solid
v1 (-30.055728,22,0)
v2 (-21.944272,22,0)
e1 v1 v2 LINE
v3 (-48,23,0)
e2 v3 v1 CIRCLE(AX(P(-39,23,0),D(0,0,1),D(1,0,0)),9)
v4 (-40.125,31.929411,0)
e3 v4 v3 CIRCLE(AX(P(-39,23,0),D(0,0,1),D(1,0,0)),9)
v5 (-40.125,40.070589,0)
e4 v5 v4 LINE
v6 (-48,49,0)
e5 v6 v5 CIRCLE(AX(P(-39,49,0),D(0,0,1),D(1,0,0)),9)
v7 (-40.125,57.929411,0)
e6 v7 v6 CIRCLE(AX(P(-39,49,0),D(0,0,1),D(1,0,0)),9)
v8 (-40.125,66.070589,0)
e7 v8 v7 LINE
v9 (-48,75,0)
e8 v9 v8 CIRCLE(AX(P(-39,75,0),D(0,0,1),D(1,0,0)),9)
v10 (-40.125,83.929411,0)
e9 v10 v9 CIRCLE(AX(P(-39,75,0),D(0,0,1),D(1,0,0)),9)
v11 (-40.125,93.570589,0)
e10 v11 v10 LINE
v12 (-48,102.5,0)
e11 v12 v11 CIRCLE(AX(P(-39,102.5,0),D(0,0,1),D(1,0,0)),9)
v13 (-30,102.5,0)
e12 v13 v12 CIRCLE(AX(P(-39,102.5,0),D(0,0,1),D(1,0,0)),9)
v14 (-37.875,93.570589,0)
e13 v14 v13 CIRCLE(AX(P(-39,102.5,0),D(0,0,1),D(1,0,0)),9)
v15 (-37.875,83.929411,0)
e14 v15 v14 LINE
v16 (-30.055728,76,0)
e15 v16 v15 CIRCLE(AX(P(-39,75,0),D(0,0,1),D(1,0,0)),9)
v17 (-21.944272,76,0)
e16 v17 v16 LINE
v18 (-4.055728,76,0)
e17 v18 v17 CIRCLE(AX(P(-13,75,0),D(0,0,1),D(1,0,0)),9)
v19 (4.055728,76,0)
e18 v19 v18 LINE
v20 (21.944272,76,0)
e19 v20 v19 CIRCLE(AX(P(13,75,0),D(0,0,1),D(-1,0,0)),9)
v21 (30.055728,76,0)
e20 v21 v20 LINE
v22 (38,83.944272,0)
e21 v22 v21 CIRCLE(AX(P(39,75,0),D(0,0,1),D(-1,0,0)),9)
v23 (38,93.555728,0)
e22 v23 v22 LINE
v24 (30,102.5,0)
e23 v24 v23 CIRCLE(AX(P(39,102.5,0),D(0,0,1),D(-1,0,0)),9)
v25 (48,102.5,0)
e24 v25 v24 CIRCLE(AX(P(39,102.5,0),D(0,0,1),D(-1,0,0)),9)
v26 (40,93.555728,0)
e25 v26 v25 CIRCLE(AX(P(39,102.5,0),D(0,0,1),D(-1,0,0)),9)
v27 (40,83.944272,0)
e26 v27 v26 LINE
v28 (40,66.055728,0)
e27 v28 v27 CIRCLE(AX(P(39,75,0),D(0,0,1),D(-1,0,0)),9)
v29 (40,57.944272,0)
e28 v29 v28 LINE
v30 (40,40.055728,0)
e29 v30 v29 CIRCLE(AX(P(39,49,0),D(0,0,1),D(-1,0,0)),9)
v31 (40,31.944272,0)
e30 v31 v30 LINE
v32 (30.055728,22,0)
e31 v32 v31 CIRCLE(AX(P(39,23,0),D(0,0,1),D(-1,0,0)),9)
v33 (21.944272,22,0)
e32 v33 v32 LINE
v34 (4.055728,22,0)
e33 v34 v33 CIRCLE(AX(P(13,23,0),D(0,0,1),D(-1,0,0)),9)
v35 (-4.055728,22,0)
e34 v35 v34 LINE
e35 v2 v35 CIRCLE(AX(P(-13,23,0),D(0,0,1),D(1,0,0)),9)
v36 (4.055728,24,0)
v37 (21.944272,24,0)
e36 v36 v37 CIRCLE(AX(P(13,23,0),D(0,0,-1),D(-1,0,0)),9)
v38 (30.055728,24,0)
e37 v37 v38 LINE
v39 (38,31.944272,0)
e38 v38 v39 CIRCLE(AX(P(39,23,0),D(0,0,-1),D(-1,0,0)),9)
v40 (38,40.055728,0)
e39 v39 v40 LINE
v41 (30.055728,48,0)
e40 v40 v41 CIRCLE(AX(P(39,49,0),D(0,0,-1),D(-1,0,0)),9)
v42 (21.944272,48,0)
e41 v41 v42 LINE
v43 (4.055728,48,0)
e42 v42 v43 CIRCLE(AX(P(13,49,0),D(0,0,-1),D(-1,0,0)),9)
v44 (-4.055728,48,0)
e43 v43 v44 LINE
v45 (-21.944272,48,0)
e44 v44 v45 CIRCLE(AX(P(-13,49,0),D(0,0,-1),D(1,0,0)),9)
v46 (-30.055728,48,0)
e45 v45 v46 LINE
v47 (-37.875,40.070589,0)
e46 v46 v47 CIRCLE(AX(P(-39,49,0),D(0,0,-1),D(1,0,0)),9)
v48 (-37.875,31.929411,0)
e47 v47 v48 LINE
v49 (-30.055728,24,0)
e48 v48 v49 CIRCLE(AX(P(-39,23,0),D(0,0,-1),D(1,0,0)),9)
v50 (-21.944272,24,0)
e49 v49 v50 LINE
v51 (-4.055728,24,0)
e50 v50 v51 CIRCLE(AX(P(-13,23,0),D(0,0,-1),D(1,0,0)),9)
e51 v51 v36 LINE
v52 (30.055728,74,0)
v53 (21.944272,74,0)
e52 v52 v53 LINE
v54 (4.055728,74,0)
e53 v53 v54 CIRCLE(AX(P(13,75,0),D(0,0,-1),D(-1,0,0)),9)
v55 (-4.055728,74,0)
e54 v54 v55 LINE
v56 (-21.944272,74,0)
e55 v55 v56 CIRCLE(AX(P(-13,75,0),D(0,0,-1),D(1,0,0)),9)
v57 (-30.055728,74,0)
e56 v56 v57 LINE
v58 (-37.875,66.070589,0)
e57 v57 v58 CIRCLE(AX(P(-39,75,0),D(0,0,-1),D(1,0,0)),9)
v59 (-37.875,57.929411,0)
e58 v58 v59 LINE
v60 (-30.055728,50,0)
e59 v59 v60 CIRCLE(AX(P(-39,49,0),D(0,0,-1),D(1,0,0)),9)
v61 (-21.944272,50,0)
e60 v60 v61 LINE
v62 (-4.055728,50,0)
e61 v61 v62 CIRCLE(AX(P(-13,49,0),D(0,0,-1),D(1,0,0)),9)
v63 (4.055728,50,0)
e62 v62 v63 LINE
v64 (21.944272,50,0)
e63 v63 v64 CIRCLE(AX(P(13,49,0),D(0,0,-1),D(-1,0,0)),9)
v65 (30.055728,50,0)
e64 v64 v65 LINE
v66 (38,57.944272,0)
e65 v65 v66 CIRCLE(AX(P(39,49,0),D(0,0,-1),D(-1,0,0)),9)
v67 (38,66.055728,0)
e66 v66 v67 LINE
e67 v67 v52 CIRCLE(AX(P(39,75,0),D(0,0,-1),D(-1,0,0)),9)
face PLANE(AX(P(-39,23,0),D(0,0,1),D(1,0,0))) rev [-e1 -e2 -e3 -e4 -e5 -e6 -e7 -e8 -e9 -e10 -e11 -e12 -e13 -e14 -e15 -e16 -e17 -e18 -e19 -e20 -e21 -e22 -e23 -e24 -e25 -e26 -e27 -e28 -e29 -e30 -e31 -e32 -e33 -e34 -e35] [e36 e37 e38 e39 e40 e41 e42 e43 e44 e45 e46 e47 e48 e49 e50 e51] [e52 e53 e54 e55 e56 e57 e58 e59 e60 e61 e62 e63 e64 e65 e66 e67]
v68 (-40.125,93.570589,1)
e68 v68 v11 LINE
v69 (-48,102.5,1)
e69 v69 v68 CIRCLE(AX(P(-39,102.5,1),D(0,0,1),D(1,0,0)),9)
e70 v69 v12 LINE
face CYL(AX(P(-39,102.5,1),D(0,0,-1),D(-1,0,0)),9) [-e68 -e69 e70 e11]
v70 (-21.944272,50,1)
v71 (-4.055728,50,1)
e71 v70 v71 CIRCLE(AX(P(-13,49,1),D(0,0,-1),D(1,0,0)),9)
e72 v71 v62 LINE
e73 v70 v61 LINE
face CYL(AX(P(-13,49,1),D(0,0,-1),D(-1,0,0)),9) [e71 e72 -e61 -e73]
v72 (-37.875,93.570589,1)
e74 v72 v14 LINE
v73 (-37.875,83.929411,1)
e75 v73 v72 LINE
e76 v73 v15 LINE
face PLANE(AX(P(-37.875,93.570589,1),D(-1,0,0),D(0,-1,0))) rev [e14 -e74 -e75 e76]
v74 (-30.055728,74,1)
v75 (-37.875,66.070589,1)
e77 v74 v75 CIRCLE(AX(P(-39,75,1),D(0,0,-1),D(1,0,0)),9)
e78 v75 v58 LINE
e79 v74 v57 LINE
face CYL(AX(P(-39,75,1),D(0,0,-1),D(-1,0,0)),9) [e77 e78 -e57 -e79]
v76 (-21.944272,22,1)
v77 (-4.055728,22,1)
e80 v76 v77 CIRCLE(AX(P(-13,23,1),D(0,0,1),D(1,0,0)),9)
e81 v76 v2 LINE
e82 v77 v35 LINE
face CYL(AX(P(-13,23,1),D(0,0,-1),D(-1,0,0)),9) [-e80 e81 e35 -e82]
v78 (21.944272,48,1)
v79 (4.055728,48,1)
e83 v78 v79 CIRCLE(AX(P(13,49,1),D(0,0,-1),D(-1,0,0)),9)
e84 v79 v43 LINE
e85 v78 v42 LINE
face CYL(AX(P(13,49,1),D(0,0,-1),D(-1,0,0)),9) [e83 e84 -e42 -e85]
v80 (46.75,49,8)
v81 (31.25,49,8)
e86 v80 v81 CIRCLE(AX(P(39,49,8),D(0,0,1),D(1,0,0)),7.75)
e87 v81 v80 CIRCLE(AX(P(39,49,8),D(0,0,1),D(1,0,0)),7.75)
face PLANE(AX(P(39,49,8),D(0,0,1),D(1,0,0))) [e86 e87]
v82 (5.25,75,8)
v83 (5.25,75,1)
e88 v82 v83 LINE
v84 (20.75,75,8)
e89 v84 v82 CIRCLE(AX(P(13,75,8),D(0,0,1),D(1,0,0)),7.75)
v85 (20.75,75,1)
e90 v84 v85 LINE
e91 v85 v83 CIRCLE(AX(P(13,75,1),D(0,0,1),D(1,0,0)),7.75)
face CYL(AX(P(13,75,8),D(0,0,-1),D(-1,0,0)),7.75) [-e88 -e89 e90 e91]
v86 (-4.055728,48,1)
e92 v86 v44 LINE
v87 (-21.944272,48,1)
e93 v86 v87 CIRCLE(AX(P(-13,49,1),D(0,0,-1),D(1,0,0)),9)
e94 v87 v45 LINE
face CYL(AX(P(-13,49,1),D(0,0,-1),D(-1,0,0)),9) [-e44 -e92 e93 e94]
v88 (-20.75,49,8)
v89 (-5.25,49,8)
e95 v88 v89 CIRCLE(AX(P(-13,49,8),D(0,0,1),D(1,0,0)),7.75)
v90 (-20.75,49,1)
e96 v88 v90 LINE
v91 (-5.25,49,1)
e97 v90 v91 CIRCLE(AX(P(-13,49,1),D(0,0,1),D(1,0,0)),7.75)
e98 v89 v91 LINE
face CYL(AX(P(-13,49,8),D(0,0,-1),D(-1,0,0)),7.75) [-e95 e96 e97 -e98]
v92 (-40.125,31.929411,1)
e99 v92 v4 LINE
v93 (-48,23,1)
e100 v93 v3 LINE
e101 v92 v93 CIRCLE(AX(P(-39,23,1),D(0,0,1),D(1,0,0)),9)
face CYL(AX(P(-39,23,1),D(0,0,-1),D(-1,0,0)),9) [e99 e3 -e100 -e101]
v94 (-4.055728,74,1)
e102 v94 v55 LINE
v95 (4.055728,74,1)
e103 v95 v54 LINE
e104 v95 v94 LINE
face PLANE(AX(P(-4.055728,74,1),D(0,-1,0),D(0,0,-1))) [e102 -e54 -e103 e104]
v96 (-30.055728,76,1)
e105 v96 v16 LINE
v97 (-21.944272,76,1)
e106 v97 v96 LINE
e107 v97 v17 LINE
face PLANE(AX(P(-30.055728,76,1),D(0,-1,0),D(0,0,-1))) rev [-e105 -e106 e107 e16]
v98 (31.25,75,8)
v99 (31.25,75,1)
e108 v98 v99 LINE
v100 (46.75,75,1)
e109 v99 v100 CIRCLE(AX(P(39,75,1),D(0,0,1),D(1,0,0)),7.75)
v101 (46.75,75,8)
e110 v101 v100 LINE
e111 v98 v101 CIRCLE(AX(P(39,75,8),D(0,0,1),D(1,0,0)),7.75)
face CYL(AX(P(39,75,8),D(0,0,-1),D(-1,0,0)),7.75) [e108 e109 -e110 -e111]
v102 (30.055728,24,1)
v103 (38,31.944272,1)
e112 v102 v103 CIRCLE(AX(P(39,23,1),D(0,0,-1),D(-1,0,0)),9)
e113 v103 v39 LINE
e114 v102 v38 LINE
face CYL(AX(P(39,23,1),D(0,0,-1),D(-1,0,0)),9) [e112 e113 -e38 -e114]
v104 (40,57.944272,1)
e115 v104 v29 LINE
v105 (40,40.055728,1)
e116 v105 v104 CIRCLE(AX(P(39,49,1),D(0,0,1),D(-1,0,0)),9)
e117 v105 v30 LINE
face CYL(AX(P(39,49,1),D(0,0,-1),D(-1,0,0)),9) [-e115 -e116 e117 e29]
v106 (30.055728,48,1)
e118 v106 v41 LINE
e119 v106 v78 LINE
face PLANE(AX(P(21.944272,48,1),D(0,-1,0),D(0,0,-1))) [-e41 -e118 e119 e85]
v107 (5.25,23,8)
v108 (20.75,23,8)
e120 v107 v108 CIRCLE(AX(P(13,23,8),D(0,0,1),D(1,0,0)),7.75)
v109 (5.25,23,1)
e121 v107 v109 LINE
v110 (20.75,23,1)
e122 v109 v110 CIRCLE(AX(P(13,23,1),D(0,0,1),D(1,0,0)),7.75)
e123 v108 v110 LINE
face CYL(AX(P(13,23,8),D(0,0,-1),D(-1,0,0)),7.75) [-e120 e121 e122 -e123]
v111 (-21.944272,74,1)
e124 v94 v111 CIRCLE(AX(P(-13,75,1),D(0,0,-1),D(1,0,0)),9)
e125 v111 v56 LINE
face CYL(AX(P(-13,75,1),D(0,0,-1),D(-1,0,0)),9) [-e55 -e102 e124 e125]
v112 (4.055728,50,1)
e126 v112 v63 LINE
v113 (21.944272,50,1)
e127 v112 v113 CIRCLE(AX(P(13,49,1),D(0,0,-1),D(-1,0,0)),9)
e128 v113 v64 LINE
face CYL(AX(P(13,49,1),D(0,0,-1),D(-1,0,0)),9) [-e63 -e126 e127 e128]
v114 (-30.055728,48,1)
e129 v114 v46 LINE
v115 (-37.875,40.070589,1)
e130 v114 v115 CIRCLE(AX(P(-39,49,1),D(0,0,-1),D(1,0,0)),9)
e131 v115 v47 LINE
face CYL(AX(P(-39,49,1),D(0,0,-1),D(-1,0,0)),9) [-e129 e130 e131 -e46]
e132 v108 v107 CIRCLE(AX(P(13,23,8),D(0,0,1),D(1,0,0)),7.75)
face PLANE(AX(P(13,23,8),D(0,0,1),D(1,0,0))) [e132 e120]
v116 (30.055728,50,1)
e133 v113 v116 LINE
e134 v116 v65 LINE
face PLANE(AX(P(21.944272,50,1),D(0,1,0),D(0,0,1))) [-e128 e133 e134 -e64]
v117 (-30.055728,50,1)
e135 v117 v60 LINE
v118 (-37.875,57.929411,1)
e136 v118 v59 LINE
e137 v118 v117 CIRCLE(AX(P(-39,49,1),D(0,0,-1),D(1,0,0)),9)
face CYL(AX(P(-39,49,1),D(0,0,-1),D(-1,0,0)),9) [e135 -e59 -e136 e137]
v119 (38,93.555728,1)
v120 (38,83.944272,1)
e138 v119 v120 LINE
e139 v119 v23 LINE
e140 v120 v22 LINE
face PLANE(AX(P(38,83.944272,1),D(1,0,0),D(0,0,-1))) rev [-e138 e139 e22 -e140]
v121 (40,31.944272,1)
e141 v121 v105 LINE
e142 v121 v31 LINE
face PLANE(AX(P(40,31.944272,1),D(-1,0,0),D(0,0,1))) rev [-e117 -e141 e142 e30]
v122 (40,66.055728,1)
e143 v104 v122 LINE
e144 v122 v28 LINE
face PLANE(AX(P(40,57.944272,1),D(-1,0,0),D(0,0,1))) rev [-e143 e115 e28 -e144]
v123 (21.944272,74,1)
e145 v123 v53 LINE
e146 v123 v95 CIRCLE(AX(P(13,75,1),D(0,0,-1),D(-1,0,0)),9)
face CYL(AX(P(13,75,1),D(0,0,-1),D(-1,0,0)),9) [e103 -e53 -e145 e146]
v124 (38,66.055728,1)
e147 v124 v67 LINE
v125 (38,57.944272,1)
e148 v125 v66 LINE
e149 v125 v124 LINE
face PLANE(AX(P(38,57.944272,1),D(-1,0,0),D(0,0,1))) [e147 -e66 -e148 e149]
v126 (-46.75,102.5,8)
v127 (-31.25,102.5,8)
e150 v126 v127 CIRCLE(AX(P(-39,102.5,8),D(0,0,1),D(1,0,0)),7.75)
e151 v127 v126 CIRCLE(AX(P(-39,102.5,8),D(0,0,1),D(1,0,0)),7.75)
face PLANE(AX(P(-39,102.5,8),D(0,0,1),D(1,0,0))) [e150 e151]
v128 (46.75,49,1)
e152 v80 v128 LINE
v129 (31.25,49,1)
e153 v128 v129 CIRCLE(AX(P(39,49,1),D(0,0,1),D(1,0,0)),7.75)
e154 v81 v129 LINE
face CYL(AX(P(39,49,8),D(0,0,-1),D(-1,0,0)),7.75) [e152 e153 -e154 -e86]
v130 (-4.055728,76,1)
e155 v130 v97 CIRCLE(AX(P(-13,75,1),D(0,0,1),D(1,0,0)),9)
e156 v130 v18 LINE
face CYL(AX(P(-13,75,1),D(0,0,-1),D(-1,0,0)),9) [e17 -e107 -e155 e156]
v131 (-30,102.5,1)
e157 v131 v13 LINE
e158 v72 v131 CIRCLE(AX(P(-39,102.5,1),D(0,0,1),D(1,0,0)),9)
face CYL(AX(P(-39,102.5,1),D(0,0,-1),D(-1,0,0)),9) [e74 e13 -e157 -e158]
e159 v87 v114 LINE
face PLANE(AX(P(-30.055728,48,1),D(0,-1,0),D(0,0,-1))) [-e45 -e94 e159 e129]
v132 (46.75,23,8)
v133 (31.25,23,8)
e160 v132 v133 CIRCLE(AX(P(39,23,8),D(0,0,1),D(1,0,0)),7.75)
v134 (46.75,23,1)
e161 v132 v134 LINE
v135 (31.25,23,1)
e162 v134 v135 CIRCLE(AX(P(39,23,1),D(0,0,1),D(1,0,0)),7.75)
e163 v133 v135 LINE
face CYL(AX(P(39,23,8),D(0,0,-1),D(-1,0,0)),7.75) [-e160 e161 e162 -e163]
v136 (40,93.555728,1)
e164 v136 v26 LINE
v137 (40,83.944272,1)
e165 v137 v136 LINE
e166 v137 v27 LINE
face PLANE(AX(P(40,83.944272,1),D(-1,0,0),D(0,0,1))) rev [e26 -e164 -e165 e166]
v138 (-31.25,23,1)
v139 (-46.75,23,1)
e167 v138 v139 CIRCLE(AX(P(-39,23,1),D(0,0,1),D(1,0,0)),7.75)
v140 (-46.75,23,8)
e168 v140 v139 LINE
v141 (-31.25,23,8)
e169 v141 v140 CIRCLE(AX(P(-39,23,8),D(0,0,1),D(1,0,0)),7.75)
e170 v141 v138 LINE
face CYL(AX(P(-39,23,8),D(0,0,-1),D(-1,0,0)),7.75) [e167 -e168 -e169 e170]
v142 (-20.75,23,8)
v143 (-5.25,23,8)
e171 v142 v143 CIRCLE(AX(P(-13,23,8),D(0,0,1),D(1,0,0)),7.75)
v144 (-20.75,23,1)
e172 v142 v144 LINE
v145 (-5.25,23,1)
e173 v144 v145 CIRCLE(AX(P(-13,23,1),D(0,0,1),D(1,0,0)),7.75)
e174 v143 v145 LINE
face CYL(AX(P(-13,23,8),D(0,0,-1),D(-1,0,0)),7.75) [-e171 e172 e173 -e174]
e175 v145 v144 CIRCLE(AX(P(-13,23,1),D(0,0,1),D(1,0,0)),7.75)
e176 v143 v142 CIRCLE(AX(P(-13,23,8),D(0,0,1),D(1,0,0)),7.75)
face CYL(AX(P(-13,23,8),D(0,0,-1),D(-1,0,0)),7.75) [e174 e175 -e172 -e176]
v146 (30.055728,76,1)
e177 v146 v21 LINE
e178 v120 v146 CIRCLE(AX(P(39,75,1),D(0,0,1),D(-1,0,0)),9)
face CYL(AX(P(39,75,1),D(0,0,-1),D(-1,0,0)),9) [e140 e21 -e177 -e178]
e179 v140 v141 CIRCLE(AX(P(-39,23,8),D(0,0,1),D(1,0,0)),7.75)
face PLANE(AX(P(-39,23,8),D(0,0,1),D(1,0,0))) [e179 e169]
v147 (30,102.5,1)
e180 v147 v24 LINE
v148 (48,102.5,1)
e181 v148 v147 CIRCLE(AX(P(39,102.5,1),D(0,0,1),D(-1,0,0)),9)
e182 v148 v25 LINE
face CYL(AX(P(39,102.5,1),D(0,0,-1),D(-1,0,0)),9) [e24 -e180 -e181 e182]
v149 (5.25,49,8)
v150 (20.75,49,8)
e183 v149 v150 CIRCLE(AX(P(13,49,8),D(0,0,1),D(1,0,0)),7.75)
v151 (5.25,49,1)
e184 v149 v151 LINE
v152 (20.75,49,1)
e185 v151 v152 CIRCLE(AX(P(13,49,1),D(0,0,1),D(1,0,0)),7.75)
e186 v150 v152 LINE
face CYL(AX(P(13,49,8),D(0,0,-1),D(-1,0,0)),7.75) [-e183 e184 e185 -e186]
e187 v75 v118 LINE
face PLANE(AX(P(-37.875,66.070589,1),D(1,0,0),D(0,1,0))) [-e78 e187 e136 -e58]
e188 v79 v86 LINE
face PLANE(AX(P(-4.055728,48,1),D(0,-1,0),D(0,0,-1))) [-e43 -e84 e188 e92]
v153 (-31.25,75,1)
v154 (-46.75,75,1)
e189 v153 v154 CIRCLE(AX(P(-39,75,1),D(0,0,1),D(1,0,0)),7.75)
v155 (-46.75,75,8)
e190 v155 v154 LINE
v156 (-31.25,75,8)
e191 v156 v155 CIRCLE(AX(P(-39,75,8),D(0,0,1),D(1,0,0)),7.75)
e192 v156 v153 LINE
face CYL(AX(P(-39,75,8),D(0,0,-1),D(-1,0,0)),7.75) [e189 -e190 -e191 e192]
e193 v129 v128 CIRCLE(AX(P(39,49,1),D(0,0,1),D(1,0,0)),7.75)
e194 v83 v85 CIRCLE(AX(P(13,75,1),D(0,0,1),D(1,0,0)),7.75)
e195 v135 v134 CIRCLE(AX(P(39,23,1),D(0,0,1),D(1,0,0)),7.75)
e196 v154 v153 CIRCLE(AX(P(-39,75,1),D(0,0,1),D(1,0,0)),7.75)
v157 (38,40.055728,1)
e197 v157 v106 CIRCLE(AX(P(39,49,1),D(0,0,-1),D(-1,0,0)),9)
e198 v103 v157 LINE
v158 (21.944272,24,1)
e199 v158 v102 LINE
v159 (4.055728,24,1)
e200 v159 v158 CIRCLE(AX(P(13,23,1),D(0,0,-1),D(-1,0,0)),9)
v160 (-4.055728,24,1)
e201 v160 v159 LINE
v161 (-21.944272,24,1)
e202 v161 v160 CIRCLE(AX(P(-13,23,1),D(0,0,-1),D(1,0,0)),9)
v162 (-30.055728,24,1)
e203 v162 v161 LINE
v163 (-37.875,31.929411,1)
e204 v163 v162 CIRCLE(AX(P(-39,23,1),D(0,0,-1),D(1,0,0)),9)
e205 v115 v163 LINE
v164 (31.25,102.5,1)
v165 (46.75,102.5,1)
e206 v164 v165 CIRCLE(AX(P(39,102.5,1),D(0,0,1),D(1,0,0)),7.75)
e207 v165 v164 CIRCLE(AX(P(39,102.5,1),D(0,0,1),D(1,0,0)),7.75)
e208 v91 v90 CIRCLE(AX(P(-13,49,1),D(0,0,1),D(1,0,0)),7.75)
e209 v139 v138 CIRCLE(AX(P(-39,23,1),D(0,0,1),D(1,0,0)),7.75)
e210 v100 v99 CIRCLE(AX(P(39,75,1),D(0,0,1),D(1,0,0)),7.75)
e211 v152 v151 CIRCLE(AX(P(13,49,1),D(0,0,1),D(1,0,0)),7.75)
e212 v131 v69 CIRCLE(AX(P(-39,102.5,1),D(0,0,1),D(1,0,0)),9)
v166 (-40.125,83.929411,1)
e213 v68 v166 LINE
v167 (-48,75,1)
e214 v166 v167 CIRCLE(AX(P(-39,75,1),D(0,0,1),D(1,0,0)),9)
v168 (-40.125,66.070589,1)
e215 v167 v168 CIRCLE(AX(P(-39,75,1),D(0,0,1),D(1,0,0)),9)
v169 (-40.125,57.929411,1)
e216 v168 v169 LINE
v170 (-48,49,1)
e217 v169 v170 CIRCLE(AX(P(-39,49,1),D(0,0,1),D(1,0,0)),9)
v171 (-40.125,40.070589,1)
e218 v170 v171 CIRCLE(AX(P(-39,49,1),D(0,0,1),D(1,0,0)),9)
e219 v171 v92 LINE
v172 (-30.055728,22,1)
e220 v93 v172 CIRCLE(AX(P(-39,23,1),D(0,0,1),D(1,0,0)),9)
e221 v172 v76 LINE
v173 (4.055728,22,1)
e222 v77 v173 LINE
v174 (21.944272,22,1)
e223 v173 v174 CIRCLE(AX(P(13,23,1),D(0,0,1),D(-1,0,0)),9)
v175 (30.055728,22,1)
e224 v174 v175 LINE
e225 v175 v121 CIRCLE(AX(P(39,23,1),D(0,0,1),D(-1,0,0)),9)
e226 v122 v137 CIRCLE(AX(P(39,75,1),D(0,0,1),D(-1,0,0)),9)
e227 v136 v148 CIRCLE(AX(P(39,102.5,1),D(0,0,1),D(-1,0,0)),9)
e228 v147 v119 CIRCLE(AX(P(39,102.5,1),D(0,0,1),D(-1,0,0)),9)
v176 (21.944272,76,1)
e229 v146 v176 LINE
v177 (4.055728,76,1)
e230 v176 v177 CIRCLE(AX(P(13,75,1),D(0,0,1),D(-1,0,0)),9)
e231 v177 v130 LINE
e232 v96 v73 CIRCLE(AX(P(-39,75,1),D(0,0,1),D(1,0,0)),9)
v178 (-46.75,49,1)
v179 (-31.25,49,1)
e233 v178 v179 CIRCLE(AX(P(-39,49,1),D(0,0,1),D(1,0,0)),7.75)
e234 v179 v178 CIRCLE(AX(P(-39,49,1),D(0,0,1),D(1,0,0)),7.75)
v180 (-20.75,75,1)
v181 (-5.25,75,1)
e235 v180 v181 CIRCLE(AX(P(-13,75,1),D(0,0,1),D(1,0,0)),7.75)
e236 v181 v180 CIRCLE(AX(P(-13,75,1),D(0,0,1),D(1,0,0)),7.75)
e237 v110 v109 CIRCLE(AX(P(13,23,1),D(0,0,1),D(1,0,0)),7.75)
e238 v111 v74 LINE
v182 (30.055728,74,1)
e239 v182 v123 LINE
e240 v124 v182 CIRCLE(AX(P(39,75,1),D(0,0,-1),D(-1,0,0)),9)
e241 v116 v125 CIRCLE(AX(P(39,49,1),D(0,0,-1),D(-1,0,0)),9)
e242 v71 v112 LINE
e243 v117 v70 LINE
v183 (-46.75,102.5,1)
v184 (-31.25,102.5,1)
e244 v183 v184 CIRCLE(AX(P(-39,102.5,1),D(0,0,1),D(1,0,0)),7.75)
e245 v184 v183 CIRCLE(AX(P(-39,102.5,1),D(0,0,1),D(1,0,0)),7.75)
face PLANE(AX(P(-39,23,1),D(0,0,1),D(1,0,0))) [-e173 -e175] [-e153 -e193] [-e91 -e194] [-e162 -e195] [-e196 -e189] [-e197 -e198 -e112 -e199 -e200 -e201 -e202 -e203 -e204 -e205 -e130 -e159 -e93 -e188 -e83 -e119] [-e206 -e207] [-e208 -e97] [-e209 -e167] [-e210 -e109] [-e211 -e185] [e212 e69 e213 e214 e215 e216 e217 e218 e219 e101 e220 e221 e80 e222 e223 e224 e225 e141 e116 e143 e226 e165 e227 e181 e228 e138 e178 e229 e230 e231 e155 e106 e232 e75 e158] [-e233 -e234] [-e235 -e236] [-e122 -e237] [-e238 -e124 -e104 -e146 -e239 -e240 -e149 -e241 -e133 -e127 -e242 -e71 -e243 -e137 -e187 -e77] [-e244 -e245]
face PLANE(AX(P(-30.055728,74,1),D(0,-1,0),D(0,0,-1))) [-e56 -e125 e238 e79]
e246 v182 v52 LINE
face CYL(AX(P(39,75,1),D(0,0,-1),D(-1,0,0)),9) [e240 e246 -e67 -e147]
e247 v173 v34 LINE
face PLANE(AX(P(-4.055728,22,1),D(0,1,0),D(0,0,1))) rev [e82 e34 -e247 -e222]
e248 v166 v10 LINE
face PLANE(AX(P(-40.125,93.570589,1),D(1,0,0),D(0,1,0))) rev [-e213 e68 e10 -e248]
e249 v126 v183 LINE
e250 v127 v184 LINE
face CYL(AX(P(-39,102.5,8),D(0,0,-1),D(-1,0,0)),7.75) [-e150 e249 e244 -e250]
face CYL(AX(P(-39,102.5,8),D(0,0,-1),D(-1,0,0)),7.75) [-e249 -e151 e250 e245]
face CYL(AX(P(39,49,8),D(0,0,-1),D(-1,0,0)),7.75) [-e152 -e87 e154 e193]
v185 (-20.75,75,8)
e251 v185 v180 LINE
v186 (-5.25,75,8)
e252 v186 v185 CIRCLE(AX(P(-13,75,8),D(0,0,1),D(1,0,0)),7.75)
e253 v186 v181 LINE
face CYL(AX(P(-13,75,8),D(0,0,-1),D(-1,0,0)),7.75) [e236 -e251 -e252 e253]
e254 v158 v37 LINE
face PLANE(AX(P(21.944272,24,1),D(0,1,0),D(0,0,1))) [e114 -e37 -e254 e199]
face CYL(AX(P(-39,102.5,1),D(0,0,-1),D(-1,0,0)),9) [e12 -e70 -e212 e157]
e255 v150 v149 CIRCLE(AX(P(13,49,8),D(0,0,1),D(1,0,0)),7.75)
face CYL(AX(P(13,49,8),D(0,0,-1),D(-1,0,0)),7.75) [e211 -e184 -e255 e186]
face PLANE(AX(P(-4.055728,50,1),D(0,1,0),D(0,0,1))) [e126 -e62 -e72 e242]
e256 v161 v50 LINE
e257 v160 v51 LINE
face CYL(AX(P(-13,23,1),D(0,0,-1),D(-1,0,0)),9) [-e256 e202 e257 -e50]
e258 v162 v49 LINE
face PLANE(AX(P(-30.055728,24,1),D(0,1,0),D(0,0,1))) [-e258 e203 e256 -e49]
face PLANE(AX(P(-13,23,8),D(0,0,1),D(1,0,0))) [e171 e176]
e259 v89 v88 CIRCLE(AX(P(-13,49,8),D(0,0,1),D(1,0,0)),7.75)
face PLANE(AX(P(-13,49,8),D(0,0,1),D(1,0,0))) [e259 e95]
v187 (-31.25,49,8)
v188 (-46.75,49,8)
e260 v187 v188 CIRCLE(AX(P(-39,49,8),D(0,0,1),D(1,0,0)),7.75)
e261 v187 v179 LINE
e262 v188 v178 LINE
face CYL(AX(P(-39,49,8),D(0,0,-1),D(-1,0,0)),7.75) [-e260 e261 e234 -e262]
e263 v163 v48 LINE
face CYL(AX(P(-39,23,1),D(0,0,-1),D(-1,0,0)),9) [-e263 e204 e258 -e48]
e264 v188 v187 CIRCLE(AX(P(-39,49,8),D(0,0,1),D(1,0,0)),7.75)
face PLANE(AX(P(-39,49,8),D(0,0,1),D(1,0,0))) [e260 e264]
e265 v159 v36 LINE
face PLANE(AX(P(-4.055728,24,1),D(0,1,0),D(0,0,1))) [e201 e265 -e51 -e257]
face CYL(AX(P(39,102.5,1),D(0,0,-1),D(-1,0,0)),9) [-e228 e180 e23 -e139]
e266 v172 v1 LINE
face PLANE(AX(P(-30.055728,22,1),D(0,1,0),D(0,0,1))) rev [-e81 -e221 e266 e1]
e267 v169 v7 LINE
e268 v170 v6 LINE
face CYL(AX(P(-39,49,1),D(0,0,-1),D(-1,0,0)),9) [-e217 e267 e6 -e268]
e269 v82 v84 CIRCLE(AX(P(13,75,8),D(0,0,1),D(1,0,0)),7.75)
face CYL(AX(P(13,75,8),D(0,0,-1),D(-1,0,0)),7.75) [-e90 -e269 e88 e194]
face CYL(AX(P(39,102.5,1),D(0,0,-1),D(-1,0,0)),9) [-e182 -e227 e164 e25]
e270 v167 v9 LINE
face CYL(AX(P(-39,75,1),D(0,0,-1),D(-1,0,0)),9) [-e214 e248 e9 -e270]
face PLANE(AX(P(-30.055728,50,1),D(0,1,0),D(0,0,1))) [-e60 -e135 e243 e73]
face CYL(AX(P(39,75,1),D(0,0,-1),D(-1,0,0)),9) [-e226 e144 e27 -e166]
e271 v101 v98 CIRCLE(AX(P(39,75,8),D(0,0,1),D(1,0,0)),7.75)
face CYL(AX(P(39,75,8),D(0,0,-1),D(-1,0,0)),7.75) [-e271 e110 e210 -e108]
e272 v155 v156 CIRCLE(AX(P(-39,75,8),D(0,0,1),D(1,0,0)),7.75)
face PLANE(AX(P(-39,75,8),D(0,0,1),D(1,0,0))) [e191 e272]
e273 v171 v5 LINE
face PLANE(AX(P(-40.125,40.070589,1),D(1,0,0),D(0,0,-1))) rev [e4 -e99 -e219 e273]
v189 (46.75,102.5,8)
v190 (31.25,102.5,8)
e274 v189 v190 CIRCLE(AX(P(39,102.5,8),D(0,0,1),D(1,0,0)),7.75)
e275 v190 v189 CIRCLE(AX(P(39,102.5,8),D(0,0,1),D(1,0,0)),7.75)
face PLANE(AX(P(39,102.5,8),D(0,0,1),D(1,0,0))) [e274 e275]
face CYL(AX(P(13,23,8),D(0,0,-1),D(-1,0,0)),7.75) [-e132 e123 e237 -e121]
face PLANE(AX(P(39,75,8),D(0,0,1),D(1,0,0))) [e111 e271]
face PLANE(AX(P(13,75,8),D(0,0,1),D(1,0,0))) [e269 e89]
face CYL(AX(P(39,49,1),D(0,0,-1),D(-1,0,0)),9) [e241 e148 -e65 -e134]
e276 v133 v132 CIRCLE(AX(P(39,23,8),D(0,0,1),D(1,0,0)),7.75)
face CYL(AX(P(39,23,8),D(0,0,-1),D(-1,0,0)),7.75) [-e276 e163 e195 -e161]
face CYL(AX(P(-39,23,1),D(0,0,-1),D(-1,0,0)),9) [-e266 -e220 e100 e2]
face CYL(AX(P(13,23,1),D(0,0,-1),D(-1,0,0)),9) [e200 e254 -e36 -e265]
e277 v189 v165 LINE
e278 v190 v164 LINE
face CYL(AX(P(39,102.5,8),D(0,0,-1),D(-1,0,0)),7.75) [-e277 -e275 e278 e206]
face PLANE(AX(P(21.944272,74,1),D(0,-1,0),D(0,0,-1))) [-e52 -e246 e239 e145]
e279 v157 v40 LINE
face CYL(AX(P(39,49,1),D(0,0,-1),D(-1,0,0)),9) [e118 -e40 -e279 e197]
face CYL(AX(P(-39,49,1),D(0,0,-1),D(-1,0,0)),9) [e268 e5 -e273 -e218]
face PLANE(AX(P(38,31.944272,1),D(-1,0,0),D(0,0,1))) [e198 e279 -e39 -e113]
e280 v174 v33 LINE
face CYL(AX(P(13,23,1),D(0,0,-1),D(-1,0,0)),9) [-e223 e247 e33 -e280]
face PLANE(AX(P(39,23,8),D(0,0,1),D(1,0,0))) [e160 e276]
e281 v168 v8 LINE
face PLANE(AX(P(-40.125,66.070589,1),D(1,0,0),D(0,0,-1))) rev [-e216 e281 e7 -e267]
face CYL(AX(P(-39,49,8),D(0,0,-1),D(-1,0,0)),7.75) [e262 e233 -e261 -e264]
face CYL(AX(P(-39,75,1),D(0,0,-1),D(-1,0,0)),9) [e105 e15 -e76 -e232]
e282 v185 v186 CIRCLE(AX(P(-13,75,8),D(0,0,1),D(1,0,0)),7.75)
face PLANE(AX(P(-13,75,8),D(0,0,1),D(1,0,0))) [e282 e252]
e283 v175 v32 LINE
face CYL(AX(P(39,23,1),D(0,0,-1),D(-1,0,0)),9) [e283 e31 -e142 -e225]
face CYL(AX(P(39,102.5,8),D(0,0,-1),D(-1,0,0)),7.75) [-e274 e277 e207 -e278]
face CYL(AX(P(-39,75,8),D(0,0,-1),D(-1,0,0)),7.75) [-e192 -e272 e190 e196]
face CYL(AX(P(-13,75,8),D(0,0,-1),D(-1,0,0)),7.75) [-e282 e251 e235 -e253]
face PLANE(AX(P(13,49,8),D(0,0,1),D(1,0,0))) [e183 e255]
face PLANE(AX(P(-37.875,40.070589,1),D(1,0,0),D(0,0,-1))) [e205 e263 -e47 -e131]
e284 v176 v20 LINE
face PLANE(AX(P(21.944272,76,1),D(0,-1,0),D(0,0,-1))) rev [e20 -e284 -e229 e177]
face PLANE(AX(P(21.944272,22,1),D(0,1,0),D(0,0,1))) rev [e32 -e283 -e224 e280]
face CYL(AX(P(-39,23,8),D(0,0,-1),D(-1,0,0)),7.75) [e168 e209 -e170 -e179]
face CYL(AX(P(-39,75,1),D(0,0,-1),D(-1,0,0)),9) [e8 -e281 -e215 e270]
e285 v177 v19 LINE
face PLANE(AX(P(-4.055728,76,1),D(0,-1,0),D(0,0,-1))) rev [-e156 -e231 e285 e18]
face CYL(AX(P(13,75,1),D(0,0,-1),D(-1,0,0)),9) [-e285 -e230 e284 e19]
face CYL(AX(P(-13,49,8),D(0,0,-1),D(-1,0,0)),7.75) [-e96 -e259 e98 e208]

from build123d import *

# Parameters (mm, degrees)
BOSS_EXTRUDE1_DEPTH = 1
SKETCH2_R           = 7.75
BOSS_EXTRUDE2_DEPTH = 7


with BuildPart() as part:
    # Sketch1 → Boss-Extrude1 (new body)
    with BuildSketch(Plane.XY):
        with BuildLine():
            Line((-40.125, 93.570589325), (-40.125, 83.929410675))
            ThreePointArc((-40.125, 83.929410675), (-48, 75), (-40.125, 66.070589325))
            Line((-40.125, 66.070589325), (-40.125, 57.929410675))
            ThreePointArc((-40.125, 57.929410675), (-48, 49), (-40.125, 40.070589325))
            Line((-40.125, 40.070589325), (-40.125, 31.929410675))
            ThreePointArc((-40.125, 31.929410675), (-45.319299992, 16.591689176), (-30.05572809, 22))
            Line((-30.05572809, 22), (-21.94427191, 22))
            ThreePointArc((-21.94427191, 22), (-13, 14), (-4.05572809, 22))
            Line((-4.05572809, 22), (4.05572809, 22))
            ThreePointArc((4.05572809, 22), (13, 14), (21.94427191, 22))
            Line((21.94427191, 22), (30.05572809, 22))
            ThreePointArc((30.05572809, 22), (45.363961031, 16.636038969), (40, 31.94427191))
            Line((40, 31.94427191), (40, 40.05572809))
            ThreePointArc((40, 40.05572809), (48, 49), (40, 57.94427191))
            Line((40, 57.94427191), (40, 66.05572809))
            ThreePointArc((40, 66.05572809), (48, 75), (40, 83.94427191))
            Line((40, 83.94427191), (40, 93.55572809))
            ThreePointArc((40, 93.55572809), (39, 111.5), (38, 93.55572809))
            Line((38, 93.55572809), (38, 83.94427191))
            ThreePointArc((38, 83.94427191), (32.636038969, 81.363961031), (30.05572809, 76))
            Line((30.05572809, 76), (21.94427191, 76))
            ThreePointArc((21.94427191, 76), (13, 84), (4.05572809, 76))
            Line((4.05572809, 76), (-4.05572809, 76))
            ThreePointArc((-4.05572809, 76), (-13, 84), (-21.94427191, 76))
            Line((-21.94427191, 76), (-30.05572809, 76))
            ThreePointArc((-30.05572809, 76), (-32.591689176, 81.319299992), (-37.875, 83.929410675))
            Line((-37.875, 83.929410675), (-37.875, 93.570589325))
            ThreePointArc((-37.875, 93.570589325), (-39, 111.5), (-40.125, 93.570589325))
        make_face()
        with BuildLine():
            Line((-30.05572809, 74), (-21.94427191, 74))
            ThreePointArc((-21.94427191, 74), (-13, 66), (-4.05572809, 74))
            Line((-4.05572809, 74), (4.05572809, 74))
            ThreePointArc((4.05572809, 74), (13, 66), (21.94427191, 74))
            Line((21.94427191, 74), (30.05572809, 74))
            ThreePointArc((30.05572809, 74), (32.636038969, 68.636038969), (38, 66.05572809))
            Line((38, 66.05572809), (38, 57.94427191))
            ThreePointArc((38, 57.94427191), (32.636038969, 55.363961031), (30.05572809, 50))
            Line((30.05572809, 50), (21.94427191, 50))
            ThreePointArc((21.94427191, 50), (13, 58), (4.05572809, 50))
            Line((4.05572809, 50), (-4.05572809, 50))
            ThreePointArc((-4.05572809, 50), (-13, 58), (-21.94427191, 50))
            Line((-21.94427191, 50), (-30.05572809, 50))
            ThreePointArc((-30.05572809, 50), (-32.591689176, 55.319299992), (-37.875, 57.929410675))
            Line((-37.875, 57.929410675), (-37.875, 66.070589325))
            ThreePointArc((-37.875, 66.070589325), (-32.591689176, 68.680700008), (-30.05572809, 74))
        make_face(mode=Mode.SUBTRACT)
        with BuildLine():
            Line((-30.05572809, 48), (-21.94427191, 48))
            ThreePointArc((-21.94427191, 48), (-13, 40), (-4.05572809, 48))
            Line((-4.05572809, 48), (4.05572809, 48))
            ThreePointArc((4.05572809, 48), (13, 40), (21.94427191, 48))
            Line((21.94427191, 48), (30.05572809, 48))
            ThreePointArc((30.05572809, 48), (32.636038969, 42.636038969), (38, 40.05572809))
            Line((38, 40.05572809), (38, 31.94427191))
            ThreePointArc((38, 31.94427191), (32.636038969, 29.363961031), (30.05572809, 24))
            Line((30.05572809, 24), (21.94427191, 24))
            ThreePointArc((21.94427191, 24), (13, 32), (4.05572809, 24))
            Line((4.05572809, 24), (-4.05572809, 24))
            ThreePointArc((-4.05572809, 24), (-13, 32), (-21.94427191, 24))
            Line((-21.94427191, 24), (-30.05572809, 24))
            ThreePointArc((-30.05572809, 24), (-32.591689176, 29.319299992), (-37.875, 31.929410675))
            Line((-37.875, 31.929410675), (-37.875, 40.070589325))
            ThreePointArc((-37.875, 40.070589325), (-32.591689176, 42.680700008), (-30.05572809, 48))
        make_face(mode=Mode.SUBTRACT)
    extrude(amount=BOSS_EXTRUDE1_DEPTH)

    # Sketch2 → Boss-Extrude2 (add)
    with BuildSketch(Plane.XY.offset(1)):
        with Locations((-39, 102.5)):
            Circle(SKETCH2_R)
        with Locations((-39, 75)):
            Circle(SKETCH2_R)
        with Locations((-39, 49)):
            Circle(SKETCH2_R)
        with Locations((-39, 23)):
            Circle(SKETCH2_R)
        with Locations((-13, 75)):
            Circle(SKETCH2_R)
        with Locations((-13, 49)):
            Circle(SKETCH2_R)
        with Locations((-13, 23)):
            Circle(SKETCH2_R)
        with Locations((13, 75)):
            Circle(SKETCH2_R)
        with Locations((39, 102.5)):
            Circle(SKETCH2_R)
        with Locations((39, 23)):
            Circle(SKETCH2_R)
        with Locations((13, 23)):
            Circle(SKETCH2_R)
        with Locations((39, 49)):
            Circle(SKETCH2_R)
        with Locations((13, 49)):
            Circle(SKETCH2_R)
        with Locations((39, 75)):
            Circle(SKETCH2_R)
    extrude(amount=BOSS_EXTRUDE2_DEPTH)


solid = part.part
